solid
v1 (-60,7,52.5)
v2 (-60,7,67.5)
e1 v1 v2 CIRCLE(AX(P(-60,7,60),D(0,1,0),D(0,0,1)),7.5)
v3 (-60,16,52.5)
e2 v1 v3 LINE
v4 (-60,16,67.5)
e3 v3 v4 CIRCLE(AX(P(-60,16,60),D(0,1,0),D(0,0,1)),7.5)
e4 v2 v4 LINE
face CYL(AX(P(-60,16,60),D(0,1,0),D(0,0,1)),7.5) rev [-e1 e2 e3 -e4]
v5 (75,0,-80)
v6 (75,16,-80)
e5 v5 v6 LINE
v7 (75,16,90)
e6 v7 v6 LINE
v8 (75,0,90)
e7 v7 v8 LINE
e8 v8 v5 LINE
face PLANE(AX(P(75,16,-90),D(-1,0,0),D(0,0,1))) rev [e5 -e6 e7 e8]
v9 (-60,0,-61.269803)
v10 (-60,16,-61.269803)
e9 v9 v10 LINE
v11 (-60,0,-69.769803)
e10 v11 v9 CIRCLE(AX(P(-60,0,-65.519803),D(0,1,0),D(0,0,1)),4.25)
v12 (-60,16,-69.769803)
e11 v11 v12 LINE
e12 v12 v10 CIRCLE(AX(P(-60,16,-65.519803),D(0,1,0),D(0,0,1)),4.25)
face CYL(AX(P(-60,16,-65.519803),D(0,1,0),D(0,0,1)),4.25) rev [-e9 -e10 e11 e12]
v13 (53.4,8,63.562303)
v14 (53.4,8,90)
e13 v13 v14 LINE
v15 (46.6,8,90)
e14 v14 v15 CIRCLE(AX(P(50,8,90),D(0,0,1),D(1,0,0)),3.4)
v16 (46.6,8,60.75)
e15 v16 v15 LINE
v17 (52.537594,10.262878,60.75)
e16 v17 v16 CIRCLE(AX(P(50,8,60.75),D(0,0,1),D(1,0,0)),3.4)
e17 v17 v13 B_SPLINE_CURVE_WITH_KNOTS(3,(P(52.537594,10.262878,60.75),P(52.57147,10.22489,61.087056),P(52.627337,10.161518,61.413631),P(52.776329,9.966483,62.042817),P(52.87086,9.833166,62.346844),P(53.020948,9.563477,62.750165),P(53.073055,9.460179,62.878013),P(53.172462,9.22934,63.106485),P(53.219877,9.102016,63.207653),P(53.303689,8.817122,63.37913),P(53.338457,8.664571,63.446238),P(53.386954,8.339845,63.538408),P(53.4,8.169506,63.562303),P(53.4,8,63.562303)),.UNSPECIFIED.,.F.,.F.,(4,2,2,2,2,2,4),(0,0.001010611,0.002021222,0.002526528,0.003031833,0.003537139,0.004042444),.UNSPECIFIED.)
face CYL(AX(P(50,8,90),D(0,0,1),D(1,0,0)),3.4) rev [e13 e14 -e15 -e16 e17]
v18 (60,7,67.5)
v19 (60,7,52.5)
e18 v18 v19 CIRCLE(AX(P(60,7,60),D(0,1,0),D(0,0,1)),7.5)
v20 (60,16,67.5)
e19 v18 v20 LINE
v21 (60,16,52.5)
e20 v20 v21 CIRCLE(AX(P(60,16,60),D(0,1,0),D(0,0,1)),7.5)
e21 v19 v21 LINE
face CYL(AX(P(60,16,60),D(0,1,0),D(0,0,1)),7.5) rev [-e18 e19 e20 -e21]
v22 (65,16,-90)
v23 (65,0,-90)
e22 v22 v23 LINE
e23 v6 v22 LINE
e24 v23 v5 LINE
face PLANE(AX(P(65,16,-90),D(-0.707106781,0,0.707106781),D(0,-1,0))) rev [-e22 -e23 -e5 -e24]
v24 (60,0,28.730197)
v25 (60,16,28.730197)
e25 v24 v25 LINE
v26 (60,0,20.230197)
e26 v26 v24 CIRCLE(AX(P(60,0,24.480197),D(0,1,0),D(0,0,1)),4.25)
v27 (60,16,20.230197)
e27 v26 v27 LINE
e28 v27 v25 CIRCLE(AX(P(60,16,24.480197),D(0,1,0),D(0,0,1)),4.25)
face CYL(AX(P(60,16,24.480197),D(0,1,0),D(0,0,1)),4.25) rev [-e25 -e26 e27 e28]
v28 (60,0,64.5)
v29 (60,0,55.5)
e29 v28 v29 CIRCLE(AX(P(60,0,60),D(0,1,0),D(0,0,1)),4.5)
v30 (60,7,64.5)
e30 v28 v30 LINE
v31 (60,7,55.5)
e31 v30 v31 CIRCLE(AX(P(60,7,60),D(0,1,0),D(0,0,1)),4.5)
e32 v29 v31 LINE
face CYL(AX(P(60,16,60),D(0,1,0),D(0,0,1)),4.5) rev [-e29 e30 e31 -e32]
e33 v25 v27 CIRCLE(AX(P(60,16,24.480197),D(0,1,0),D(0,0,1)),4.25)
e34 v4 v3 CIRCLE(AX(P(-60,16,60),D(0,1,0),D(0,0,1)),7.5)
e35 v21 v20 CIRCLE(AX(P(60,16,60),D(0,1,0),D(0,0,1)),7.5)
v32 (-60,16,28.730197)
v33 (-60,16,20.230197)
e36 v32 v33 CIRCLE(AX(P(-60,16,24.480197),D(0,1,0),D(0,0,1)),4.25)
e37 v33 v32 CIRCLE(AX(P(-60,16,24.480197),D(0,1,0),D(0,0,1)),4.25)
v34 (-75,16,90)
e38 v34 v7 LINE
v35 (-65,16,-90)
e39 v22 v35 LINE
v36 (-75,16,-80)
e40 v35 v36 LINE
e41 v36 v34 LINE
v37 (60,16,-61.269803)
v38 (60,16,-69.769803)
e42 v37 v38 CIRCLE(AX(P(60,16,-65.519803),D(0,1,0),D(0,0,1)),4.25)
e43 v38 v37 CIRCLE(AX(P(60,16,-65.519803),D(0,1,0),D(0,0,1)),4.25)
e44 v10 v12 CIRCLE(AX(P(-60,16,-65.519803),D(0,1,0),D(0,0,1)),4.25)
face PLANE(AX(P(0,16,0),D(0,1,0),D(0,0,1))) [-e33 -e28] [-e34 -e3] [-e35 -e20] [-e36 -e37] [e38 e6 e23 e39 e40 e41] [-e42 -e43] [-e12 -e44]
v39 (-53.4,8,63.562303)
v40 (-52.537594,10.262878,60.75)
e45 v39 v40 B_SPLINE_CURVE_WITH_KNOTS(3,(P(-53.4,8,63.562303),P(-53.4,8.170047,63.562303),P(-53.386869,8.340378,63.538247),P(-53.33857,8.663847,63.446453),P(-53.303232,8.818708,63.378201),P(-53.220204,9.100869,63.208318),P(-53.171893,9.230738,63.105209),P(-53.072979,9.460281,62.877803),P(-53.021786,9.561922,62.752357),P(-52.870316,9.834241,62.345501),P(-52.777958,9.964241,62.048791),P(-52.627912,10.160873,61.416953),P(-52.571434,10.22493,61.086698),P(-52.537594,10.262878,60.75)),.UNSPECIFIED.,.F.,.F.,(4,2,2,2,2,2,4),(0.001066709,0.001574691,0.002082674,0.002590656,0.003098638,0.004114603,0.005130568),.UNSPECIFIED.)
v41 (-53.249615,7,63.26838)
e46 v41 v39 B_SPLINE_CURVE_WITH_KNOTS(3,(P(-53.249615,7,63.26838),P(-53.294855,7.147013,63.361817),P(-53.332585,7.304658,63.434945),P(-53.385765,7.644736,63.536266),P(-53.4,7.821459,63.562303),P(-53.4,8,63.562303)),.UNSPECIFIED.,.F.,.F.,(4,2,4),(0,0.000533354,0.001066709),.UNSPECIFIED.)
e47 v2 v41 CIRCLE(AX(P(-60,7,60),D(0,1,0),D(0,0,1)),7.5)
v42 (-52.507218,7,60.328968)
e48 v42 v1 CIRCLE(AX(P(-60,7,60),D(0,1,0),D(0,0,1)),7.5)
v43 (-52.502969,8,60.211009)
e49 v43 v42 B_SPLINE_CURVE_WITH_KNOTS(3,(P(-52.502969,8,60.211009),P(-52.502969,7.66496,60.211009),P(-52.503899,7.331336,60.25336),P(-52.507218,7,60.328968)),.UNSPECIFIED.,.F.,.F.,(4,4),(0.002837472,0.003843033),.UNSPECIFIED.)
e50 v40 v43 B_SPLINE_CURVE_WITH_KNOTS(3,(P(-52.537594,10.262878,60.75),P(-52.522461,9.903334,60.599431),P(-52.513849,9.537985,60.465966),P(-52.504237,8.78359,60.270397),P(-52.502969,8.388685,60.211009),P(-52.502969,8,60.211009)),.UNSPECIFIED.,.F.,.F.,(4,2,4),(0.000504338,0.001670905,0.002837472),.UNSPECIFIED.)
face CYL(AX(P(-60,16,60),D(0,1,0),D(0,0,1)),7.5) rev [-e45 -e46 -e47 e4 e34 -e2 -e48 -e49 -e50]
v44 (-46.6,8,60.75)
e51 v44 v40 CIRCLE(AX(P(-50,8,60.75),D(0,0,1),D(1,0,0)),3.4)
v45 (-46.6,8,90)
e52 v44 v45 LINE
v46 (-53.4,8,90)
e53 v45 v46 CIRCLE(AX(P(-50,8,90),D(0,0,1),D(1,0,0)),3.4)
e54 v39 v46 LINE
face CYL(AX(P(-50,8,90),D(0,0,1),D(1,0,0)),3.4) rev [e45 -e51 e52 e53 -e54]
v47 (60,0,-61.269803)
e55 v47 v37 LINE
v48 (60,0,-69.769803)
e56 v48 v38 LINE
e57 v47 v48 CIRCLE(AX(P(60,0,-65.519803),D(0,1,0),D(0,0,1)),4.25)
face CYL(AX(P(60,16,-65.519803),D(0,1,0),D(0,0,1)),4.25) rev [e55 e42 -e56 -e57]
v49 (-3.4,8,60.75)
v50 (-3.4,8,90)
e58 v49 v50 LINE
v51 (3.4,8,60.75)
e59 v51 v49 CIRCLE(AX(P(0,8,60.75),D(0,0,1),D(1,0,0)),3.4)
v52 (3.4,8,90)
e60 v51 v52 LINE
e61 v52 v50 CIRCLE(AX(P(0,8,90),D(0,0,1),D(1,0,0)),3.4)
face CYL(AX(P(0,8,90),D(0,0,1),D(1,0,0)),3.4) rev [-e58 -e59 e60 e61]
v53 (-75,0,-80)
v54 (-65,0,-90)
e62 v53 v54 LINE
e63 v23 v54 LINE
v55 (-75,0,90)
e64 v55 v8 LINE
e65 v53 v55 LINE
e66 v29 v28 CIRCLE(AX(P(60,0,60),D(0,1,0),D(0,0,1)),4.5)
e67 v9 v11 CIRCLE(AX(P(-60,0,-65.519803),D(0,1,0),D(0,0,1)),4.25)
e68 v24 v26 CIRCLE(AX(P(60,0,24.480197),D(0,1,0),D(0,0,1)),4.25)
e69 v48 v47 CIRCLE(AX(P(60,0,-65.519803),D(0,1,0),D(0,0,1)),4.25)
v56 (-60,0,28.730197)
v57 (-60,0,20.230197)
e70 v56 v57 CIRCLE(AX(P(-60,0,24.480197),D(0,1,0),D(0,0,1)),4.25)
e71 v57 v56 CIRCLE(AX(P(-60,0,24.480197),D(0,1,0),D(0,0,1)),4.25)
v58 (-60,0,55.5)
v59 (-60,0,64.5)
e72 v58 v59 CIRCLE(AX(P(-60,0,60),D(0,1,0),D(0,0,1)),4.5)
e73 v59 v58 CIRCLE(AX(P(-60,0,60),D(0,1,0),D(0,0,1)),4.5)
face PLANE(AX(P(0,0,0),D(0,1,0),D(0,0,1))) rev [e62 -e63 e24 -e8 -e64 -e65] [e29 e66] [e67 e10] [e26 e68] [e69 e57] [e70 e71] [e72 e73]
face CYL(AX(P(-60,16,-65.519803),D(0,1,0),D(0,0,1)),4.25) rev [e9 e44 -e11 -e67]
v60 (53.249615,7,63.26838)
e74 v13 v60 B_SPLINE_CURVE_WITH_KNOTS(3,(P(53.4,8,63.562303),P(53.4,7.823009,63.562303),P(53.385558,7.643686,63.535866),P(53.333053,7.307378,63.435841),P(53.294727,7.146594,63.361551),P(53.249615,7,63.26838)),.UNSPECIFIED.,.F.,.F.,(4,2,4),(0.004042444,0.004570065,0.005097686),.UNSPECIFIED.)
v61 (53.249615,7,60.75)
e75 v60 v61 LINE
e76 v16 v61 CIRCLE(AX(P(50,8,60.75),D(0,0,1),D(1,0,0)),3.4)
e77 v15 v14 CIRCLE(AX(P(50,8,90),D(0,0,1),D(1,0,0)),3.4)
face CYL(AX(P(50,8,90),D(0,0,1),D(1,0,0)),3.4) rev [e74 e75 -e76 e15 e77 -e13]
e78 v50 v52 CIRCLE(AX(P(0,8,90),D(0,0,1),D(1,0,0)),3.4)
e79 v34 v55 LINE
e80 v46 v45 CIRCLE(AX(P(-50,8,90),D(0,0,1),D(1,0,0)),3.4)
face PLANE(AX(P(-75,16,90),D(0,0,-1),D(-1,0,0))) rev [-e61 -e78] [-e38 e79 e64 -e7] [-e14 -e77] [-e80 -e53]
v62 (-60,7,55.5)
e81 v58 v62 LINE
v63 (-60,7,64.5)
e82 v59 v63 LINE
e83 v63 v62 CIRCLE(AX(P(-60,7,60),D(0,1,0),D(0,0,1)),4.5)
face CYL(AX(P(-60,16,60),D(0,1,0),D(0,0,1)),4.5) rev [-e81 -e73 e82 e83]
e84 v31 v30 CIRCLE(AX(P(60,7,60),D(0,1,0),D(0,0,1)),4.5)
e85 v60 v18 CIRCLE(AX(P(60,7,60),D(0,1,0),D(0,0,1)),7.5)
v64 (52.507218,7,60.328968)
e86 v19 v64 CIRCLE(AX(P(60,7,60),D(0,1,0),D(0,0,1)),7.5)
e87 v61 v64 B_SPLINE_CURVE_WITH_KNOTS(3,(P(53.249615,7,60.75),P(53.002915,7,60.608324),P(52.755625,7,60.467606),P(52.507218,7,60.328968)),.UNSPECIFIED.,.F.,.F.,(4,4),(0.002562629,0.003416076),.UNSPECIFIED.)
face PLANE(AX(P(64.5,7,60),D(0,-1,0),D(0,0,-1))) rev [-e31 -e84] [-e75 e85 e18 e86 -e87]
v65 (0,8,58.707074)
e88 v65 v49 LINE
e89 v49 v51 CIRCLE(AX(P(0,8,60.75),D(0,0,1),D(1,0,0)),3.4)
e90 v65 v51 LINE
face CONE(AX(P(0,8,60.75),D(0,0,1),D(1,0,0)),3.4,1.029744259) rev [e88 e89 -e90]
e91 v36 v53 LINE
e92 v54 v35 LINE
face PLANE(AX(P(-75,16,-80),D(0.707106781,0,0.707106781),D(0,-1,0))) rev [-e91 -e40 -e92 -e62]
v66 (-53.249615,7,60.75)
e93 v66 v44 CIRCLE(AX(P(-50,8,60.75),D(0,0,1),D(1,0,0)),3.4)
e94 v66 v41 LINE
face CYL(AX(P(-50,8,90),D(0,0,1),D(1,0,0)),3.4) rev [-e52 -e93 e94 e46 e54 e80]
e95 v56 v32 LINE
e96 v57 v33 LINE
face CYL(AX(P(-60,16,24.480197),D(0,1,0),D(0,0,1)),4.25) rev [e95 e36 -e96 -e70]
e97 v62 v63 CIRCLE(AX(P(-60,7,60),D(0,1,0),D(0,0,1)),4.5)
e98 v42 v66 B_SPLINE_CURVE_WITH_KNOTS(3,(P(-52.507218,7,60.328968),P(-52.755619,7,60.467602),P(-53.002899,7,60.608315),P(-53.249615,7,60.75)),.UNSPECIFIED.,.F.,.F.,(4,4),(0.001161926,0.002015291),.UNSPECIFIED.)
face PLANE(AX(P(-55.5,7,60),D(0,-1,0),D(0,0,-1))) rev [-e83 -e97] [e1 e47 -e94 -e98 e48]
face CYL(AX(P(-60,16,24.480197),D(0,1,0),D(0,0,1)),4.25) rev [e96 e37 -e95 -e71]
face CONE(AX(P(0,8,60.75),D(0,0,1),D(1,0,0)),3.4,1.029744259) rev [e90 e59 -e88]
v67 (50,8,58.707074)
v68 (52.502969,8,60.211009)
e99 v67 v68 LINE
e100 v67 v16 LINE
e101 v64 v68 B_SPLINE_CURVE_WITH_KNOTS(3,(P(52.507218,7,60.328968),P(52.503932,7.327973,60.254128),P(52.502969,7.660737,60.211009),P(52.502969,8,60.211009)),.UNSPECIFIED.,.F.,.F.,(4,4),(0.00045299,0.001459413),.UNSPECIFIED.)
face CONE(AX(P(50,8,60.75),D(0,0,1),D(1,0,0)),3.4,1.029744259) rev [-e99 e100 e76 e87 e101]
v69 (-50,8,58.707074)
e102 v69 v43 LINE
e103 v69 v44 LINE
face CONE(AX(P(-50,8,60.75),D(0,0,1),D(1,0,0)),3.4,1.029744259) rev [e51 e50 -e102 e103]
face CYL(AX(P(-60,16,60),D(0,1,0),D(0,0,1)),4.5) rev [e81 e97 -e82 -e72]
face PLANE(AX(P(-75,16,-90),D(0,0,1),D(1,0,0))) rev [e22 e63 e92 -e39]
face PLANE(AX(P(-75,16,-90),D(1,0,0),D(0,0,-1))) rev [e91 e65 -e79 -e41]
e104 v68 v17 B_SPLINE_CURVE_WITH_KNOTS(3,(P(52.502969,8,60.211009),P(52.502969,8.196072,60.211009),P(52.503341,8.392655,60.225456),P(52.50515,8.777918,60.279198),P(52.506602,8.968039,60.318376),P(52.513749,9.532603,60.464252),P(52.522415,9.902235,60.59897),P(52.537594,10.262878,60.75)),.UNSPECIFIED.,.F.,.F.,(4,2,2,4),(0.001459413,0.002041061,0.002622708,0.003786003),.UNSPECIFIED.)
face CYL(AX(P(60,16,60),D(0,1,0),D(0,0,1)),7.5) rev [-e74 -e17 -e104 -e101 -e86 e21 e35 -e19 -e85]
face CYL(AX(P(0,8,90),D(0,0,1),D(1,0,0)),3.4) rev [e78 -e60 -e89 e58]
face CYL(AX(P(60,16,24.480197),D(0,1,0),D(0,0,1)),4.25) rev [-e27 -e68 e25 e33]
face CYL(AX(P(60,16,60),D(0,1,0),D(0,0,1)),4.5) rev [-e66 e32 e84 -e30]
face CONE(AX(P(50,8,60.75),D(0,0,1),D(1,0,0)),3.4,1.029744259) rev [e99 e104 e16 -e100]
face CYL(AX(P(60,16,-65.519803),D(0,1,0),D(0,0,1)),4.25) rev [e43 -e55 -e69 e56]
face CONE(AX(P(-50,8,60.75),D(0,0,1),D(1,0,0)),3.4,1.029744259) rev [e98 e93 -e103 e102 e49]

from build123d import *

# Parameters (mm, degrees)
SKETCH_1_W                = 150
SKETCH_1_H                = 180
EXTRUDE_1_DEPTH           = 16
HOLE_WIZARD_M8_1_D        = 6.8
HOLE_WIZARD_M8_1_DEPTH    = 29.25
HOLE_WIZARD_M8_1_TIP      = 2.042926105
HOLE_WIZARD_1_D           = 9
HOLE_WIZARD_1_DEPTH       = 29.25
HOLE_WIZARD_1_CBORE_D     = 15
HOLE_WIZARD_1_CBORE_DEPTH = 9
HOLE_WIZARD_1_TIP         = 2.703872786
HOLE_WIZARD_M10_1_D       = 8.5
CHAMFER_1_SIZE            = 10


with BuildPart() as part:
    # 草图1 → 凸台-拉伸1 (new body)
    with BuildSketch(Plane(origin=(0, 0, 0), x_dir=(1, 0, 0), z_dir=(0, 1, 0))):
        Rectangle(SKETCH_1_W, SKETCH_1_H)
    extrude(amount=EXTRUDE_1_DEPTH)

    # M8 螺纹孔1
    with Locations(Plane.XY.offset(90)):
        with Locations((-50, 8), (0, 8), (50, 8)):
            Hole(HOLE_WIZARD_M8_1_D / 2, depth=HOLE_WIZARD_M8_1_DEPTH)
            with Locations((0, 0, -(HOLE_WIZARD_M8_1_DEPTH + HOLE_WIZARD_M8_1_TIP / 2))):  # 118° drill point
                Cone(0, HOLE_WIZARD_M8_1_D / 2, HOLE_WIZARD_M8_1_TIP, mode=Mode.SUBTRACT)

    # 打孔尺寸(%根据)内六角圆柱头螺钉的类型1
    with Locations(Plane(origin=(0, 16, 0), x_dir=(1, 0, 0), z_dir=(0, 1, 0))):
        with Locations((-60, -60), (60, -60)):
            CounterBoreHole(HOLE_WIZARD_1_D / 2, HOLE_WIZARD_1_CBORE_D / 2, HOLE_WIZARD_1_CBORE_DEPTH, depth=HOLE_WIZARD_1_DEPTH)
            with Locations((0, 0, -(HOLE_WIZARD_1_DEPTH + HOLE_WIZARD_1_TIP / 2))):  # 118° drill point
                Cone(0, HOLE_WIZARD_1_D / 2, HOLE_WIZARD_1_TIP, mode=Mode.SUBTRACT)

    # M10 螺纹孔1 (through all)
    with Locations(Plane(origin=(0, 16, 0), x_dir=(1, 0, 0), z_dir=(0, 1, 0))):
        with Locations((-60, 65.51980275), (60, 65.51980275), (-60, -24.48019725), (60, -24.48019725)):
            Hole(HOLE_WIZARD_M10_1_D / 2)

    # 倒角1
    chamfer_1_edges = [part.edges().sort_by_distance(p)[0] for p in [
        (-75, 8, -90),
        (75, 8, -90),
    ]]
    chamfer(chamfer_1_edges, length=CHAMFER_1_SIZE)


solid = part.part
